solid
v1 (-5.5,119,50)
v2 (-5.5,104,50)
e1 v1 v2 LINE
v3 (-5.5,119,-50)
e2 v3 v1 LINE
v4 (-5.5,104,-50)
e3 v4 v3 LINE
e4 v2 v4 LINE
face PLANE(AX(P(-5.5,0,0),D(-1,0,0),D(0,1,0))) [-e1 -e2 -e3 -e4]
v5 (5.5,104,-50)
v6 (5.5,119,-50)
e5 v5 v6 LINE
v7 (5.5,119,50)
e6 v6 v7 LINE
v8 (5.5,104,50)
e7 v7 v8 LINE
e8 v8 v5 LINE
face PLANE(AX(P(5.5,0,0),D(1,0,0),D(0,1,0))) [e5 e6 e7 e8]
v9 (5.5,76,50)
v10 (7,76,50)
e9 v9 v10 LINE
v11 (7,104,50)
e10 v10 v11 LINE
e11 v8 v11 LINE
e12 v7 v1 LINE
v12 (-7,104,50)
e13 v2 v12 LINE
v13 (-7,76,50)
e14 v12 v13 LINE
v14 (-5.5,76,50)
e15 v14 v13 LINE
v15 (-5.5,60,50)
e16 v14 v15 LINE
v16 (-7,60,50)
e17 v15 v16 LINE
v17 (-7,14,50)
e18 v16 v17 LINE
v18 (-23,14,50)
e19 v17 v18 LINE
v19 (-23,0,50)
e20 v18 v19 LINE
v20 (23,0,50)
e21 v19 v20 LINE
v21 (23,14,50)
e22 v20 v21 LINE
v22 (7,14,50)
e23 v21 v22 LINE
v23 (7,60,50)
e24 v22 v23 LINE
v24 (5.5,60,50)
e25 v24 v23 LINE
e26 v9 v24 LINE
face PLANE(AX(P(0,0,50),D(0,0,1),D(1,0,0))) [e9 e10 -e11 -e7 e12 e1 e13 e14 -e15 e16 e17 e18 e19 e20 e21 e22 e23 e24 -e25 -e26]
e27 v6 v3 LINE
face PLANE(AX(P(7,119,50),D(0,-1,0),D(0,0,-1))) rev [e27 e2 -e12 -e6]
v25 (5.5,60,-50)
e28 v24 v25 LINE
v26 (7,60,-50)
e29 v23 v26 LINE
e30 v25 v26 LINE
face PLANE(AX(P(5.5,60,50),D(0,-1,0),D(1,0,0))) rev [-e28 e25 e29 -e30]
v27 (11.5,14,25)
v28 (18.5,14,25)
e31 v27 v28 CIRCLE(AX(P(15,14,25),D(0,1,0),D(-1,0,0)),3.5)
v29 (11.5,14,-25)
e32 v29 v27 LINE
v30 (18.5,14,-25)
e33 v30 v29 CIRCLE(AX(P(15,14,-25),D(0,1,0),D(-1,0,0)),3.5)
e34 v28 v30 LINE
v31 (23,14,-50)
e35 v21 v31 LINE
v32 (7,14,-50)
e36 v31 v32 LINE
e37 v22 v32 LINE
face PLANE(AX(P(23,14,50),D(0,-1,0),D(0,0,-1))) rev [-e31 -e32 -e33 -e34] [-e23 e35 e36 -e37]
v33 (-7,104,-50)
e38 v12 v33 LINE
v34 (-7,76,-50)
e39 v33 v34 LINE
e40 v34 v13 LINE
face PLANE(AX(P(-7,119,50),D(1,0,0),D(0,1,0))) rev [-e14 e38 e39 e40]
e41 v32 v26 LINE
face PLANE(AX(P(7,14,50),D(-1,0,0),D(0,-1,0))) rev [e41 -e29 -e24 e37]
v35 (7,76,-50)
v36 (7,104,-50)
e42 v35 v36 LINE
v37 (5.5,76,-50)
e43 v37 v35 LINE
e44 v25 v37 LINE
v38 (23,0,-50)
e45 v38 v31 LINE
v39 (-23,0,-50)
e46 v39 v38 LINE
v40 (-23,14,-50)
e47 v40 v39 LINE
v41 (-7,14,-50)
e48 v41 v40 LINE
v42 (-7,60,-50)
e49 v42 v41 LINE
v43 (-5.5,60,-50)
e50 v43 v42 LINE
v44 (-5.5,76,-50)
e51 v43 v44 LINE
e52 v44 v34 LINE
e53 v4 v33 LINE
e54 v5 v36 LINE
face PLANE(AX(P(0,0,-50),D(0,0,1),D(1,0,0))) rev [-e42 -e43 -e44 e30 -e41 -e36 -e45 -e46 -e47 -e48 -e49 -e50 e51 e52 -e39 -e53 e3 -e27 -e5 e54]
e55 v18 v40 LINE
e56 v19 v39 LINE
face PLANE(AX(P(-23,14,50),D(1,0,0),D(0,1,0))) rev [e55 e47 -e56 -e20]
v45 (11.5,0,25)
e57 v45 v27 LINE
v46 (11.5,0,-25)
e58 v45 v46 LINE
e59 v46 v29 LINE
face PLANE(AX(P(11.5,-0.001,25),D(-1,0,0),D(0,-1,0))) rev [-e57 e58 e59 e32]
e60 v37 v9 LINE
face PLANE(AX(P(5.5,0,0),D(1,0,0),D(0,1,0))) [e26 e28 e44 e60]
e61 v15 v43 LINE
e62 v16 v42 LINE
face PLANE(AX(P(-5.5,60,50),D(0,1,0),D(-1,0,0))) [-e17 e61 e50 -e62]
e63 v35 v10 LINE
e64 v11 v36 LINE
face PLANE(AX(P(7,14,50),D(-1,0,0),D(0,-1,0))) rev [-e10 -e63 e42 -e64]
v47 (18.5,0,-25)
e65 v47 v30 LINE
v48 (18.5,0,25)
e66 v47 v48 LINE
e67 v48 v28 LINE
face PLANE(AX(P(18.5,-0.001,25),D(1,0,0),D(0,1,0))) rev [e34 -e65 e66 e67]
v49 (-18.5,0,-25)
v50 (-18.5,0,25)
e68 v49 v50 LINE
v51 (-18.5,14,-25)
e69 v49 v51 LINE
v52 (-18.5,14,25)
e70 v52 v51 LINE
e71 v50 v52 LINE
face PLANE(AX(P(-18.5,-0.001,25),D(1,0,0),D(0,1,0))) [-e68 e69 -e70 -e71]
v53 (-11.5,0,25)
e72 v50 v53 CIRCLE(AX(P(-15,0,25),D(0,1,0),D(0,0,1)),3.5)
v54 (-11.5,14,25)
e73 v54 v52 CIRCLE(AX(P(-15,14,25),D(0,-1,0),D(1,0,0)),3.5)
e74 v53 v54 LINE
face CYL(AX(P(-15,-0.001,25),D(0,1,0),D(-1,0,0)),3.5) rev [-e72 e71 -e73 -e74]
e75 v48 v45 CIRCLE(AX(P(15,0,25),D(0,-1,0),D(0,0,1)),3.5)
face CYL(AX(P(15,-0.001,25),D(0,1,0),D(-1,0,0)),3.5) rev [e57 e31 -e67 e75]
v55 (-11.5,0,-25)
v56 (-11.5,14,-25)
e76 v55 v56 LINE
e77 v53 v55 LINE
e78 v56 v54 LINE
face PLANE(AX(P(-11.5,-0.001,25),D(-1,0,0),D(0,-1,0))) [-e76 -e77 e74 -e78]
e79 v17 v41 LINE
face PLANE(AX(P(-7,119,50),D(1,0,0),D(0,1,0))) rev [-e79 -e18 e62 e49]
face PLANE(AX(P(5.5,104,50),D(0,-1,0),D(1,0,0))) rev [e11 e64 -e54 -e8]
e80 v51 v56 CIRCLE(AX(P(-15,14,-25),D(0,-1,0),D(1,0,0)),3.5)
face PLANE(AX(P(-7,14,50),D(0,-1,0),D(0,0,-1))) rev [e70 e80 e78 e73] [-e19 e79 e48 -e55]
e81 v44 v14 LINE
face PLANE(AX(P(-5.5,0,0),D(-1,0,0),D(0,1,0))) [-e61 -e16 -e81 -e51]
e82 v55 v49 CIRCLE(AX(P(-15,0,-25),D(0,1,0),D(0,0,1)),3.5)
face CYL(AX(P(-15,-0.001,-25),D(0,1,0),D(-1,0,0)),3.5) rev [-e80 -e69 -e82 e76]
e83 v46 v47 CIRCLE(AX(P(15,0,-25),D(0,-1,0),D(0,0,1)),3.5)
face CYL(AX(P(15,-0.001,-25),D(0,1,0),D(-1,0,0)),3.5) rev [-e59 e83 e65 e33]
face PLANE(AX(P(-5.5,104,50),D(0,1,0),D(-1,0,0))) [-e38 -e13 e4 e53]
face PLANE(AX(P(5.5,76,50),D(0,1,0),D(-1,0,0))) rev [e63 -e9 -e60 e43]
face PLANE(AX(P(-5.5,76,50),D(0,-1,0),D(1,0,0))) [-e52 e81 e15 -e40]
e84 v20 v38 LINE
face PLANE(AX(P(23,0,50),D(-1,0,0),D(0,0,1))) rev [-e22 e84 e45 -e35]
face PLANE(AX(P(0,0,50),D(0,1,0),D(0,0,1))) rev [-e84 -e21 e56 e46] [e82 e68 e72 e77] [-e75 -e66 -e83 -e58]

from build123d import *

# Parameters (mm, degrees)
EXTRUDE_1_DEPTH     = 50
CUT_EXTRUDE_1_REACH = 120.55
SKETCH_3_W          = 100
SKETCH_3_H          = 15
SKETCH_3_H_2        = 16
CUT_EXTRUDE_2_DEPTH = 1.5


with BuildPart() as part:
    # 草图1 → 凸台-拉伸1 (new, symmetric)
    with BuildSketch(Plane.XY):
        Polygon((0, 0), (23, 0), (23, 14), (7, 14), (7, 119), (-7, 119), (-7, 14), (-23, 14), (-23, 0), align=None)
    extrude(amount=EXTRUDE_1_DEPTH, both=True)

    # 草图2 → 切除-拉伸1 (cut, up to next)
    with BuildSketch(Plane(origin=(0, 14, 0), x_dir=(1, 0, 0), z_dir=(0, 1, 0)), mode=Mode.PRIVATE) as cut_extrude_1_sk1:
        with BuildLine():
            Line((11.5, -25), (11.5, 25))
            ThreePointArc((11.5, 25), (15, 28.5), (18.5, 25))
            Line((18.5, 25), (18.5, -25))
            ThreePointArc((18.5, -25), (15, -28.5), (11.5, -25))
        make_face()
    cut_extrude_1_tool1 = extrude(cut_extrude_1_sk1.sketch, amount=-CUT_EXTRUDE_1_REACH, mode=Mode.PRIVATE) & part.part
    cut_extrude_1 = cut_extrude_1_tool1.solids().sort_by_distance((15, 14, 0))[0]
    add(cut_extrude_1, mode=Mode.SUBTRACT)

    # 草图3 → 切除-拉伸2 (cut)
    with BuildSketch(Plane(origin=(7, 0, 0), x_dir=(0, 0, -1), z_dir=(1, 0, 0))):
        with Locations((0, 111.5)):
            Rectangle(SKETCH_3_W, SKETCH_3_H)
        with Locations((0, 68)):
            Rectangle(SKETCH_3_W, SKETCH_3_H_2)
    cut_extrude_2 = extrude(amount=-CUT_EXTRUDE_2_DEPTH, mode=Mode.SUBTRACT)

    # 镜向1: 切除-拉伸1 across plane
    add(cut_extrude_1.mirror(Plane(origin=(0, 0, 0), x_dir=(0, 0, 1), z_dir=(1, 0, 0))), mode=Mode.SUBTRACT)

    # 镜向2: 切除-拉伸2 across plane
    add(cut_extrude_2.mirror(Plane(origin=(0, 0, 0), x_dir=(0, 0, 1), z_dir=(1, 0, 0))), mode=Mode.SUBTRACT)


solid = part.part
